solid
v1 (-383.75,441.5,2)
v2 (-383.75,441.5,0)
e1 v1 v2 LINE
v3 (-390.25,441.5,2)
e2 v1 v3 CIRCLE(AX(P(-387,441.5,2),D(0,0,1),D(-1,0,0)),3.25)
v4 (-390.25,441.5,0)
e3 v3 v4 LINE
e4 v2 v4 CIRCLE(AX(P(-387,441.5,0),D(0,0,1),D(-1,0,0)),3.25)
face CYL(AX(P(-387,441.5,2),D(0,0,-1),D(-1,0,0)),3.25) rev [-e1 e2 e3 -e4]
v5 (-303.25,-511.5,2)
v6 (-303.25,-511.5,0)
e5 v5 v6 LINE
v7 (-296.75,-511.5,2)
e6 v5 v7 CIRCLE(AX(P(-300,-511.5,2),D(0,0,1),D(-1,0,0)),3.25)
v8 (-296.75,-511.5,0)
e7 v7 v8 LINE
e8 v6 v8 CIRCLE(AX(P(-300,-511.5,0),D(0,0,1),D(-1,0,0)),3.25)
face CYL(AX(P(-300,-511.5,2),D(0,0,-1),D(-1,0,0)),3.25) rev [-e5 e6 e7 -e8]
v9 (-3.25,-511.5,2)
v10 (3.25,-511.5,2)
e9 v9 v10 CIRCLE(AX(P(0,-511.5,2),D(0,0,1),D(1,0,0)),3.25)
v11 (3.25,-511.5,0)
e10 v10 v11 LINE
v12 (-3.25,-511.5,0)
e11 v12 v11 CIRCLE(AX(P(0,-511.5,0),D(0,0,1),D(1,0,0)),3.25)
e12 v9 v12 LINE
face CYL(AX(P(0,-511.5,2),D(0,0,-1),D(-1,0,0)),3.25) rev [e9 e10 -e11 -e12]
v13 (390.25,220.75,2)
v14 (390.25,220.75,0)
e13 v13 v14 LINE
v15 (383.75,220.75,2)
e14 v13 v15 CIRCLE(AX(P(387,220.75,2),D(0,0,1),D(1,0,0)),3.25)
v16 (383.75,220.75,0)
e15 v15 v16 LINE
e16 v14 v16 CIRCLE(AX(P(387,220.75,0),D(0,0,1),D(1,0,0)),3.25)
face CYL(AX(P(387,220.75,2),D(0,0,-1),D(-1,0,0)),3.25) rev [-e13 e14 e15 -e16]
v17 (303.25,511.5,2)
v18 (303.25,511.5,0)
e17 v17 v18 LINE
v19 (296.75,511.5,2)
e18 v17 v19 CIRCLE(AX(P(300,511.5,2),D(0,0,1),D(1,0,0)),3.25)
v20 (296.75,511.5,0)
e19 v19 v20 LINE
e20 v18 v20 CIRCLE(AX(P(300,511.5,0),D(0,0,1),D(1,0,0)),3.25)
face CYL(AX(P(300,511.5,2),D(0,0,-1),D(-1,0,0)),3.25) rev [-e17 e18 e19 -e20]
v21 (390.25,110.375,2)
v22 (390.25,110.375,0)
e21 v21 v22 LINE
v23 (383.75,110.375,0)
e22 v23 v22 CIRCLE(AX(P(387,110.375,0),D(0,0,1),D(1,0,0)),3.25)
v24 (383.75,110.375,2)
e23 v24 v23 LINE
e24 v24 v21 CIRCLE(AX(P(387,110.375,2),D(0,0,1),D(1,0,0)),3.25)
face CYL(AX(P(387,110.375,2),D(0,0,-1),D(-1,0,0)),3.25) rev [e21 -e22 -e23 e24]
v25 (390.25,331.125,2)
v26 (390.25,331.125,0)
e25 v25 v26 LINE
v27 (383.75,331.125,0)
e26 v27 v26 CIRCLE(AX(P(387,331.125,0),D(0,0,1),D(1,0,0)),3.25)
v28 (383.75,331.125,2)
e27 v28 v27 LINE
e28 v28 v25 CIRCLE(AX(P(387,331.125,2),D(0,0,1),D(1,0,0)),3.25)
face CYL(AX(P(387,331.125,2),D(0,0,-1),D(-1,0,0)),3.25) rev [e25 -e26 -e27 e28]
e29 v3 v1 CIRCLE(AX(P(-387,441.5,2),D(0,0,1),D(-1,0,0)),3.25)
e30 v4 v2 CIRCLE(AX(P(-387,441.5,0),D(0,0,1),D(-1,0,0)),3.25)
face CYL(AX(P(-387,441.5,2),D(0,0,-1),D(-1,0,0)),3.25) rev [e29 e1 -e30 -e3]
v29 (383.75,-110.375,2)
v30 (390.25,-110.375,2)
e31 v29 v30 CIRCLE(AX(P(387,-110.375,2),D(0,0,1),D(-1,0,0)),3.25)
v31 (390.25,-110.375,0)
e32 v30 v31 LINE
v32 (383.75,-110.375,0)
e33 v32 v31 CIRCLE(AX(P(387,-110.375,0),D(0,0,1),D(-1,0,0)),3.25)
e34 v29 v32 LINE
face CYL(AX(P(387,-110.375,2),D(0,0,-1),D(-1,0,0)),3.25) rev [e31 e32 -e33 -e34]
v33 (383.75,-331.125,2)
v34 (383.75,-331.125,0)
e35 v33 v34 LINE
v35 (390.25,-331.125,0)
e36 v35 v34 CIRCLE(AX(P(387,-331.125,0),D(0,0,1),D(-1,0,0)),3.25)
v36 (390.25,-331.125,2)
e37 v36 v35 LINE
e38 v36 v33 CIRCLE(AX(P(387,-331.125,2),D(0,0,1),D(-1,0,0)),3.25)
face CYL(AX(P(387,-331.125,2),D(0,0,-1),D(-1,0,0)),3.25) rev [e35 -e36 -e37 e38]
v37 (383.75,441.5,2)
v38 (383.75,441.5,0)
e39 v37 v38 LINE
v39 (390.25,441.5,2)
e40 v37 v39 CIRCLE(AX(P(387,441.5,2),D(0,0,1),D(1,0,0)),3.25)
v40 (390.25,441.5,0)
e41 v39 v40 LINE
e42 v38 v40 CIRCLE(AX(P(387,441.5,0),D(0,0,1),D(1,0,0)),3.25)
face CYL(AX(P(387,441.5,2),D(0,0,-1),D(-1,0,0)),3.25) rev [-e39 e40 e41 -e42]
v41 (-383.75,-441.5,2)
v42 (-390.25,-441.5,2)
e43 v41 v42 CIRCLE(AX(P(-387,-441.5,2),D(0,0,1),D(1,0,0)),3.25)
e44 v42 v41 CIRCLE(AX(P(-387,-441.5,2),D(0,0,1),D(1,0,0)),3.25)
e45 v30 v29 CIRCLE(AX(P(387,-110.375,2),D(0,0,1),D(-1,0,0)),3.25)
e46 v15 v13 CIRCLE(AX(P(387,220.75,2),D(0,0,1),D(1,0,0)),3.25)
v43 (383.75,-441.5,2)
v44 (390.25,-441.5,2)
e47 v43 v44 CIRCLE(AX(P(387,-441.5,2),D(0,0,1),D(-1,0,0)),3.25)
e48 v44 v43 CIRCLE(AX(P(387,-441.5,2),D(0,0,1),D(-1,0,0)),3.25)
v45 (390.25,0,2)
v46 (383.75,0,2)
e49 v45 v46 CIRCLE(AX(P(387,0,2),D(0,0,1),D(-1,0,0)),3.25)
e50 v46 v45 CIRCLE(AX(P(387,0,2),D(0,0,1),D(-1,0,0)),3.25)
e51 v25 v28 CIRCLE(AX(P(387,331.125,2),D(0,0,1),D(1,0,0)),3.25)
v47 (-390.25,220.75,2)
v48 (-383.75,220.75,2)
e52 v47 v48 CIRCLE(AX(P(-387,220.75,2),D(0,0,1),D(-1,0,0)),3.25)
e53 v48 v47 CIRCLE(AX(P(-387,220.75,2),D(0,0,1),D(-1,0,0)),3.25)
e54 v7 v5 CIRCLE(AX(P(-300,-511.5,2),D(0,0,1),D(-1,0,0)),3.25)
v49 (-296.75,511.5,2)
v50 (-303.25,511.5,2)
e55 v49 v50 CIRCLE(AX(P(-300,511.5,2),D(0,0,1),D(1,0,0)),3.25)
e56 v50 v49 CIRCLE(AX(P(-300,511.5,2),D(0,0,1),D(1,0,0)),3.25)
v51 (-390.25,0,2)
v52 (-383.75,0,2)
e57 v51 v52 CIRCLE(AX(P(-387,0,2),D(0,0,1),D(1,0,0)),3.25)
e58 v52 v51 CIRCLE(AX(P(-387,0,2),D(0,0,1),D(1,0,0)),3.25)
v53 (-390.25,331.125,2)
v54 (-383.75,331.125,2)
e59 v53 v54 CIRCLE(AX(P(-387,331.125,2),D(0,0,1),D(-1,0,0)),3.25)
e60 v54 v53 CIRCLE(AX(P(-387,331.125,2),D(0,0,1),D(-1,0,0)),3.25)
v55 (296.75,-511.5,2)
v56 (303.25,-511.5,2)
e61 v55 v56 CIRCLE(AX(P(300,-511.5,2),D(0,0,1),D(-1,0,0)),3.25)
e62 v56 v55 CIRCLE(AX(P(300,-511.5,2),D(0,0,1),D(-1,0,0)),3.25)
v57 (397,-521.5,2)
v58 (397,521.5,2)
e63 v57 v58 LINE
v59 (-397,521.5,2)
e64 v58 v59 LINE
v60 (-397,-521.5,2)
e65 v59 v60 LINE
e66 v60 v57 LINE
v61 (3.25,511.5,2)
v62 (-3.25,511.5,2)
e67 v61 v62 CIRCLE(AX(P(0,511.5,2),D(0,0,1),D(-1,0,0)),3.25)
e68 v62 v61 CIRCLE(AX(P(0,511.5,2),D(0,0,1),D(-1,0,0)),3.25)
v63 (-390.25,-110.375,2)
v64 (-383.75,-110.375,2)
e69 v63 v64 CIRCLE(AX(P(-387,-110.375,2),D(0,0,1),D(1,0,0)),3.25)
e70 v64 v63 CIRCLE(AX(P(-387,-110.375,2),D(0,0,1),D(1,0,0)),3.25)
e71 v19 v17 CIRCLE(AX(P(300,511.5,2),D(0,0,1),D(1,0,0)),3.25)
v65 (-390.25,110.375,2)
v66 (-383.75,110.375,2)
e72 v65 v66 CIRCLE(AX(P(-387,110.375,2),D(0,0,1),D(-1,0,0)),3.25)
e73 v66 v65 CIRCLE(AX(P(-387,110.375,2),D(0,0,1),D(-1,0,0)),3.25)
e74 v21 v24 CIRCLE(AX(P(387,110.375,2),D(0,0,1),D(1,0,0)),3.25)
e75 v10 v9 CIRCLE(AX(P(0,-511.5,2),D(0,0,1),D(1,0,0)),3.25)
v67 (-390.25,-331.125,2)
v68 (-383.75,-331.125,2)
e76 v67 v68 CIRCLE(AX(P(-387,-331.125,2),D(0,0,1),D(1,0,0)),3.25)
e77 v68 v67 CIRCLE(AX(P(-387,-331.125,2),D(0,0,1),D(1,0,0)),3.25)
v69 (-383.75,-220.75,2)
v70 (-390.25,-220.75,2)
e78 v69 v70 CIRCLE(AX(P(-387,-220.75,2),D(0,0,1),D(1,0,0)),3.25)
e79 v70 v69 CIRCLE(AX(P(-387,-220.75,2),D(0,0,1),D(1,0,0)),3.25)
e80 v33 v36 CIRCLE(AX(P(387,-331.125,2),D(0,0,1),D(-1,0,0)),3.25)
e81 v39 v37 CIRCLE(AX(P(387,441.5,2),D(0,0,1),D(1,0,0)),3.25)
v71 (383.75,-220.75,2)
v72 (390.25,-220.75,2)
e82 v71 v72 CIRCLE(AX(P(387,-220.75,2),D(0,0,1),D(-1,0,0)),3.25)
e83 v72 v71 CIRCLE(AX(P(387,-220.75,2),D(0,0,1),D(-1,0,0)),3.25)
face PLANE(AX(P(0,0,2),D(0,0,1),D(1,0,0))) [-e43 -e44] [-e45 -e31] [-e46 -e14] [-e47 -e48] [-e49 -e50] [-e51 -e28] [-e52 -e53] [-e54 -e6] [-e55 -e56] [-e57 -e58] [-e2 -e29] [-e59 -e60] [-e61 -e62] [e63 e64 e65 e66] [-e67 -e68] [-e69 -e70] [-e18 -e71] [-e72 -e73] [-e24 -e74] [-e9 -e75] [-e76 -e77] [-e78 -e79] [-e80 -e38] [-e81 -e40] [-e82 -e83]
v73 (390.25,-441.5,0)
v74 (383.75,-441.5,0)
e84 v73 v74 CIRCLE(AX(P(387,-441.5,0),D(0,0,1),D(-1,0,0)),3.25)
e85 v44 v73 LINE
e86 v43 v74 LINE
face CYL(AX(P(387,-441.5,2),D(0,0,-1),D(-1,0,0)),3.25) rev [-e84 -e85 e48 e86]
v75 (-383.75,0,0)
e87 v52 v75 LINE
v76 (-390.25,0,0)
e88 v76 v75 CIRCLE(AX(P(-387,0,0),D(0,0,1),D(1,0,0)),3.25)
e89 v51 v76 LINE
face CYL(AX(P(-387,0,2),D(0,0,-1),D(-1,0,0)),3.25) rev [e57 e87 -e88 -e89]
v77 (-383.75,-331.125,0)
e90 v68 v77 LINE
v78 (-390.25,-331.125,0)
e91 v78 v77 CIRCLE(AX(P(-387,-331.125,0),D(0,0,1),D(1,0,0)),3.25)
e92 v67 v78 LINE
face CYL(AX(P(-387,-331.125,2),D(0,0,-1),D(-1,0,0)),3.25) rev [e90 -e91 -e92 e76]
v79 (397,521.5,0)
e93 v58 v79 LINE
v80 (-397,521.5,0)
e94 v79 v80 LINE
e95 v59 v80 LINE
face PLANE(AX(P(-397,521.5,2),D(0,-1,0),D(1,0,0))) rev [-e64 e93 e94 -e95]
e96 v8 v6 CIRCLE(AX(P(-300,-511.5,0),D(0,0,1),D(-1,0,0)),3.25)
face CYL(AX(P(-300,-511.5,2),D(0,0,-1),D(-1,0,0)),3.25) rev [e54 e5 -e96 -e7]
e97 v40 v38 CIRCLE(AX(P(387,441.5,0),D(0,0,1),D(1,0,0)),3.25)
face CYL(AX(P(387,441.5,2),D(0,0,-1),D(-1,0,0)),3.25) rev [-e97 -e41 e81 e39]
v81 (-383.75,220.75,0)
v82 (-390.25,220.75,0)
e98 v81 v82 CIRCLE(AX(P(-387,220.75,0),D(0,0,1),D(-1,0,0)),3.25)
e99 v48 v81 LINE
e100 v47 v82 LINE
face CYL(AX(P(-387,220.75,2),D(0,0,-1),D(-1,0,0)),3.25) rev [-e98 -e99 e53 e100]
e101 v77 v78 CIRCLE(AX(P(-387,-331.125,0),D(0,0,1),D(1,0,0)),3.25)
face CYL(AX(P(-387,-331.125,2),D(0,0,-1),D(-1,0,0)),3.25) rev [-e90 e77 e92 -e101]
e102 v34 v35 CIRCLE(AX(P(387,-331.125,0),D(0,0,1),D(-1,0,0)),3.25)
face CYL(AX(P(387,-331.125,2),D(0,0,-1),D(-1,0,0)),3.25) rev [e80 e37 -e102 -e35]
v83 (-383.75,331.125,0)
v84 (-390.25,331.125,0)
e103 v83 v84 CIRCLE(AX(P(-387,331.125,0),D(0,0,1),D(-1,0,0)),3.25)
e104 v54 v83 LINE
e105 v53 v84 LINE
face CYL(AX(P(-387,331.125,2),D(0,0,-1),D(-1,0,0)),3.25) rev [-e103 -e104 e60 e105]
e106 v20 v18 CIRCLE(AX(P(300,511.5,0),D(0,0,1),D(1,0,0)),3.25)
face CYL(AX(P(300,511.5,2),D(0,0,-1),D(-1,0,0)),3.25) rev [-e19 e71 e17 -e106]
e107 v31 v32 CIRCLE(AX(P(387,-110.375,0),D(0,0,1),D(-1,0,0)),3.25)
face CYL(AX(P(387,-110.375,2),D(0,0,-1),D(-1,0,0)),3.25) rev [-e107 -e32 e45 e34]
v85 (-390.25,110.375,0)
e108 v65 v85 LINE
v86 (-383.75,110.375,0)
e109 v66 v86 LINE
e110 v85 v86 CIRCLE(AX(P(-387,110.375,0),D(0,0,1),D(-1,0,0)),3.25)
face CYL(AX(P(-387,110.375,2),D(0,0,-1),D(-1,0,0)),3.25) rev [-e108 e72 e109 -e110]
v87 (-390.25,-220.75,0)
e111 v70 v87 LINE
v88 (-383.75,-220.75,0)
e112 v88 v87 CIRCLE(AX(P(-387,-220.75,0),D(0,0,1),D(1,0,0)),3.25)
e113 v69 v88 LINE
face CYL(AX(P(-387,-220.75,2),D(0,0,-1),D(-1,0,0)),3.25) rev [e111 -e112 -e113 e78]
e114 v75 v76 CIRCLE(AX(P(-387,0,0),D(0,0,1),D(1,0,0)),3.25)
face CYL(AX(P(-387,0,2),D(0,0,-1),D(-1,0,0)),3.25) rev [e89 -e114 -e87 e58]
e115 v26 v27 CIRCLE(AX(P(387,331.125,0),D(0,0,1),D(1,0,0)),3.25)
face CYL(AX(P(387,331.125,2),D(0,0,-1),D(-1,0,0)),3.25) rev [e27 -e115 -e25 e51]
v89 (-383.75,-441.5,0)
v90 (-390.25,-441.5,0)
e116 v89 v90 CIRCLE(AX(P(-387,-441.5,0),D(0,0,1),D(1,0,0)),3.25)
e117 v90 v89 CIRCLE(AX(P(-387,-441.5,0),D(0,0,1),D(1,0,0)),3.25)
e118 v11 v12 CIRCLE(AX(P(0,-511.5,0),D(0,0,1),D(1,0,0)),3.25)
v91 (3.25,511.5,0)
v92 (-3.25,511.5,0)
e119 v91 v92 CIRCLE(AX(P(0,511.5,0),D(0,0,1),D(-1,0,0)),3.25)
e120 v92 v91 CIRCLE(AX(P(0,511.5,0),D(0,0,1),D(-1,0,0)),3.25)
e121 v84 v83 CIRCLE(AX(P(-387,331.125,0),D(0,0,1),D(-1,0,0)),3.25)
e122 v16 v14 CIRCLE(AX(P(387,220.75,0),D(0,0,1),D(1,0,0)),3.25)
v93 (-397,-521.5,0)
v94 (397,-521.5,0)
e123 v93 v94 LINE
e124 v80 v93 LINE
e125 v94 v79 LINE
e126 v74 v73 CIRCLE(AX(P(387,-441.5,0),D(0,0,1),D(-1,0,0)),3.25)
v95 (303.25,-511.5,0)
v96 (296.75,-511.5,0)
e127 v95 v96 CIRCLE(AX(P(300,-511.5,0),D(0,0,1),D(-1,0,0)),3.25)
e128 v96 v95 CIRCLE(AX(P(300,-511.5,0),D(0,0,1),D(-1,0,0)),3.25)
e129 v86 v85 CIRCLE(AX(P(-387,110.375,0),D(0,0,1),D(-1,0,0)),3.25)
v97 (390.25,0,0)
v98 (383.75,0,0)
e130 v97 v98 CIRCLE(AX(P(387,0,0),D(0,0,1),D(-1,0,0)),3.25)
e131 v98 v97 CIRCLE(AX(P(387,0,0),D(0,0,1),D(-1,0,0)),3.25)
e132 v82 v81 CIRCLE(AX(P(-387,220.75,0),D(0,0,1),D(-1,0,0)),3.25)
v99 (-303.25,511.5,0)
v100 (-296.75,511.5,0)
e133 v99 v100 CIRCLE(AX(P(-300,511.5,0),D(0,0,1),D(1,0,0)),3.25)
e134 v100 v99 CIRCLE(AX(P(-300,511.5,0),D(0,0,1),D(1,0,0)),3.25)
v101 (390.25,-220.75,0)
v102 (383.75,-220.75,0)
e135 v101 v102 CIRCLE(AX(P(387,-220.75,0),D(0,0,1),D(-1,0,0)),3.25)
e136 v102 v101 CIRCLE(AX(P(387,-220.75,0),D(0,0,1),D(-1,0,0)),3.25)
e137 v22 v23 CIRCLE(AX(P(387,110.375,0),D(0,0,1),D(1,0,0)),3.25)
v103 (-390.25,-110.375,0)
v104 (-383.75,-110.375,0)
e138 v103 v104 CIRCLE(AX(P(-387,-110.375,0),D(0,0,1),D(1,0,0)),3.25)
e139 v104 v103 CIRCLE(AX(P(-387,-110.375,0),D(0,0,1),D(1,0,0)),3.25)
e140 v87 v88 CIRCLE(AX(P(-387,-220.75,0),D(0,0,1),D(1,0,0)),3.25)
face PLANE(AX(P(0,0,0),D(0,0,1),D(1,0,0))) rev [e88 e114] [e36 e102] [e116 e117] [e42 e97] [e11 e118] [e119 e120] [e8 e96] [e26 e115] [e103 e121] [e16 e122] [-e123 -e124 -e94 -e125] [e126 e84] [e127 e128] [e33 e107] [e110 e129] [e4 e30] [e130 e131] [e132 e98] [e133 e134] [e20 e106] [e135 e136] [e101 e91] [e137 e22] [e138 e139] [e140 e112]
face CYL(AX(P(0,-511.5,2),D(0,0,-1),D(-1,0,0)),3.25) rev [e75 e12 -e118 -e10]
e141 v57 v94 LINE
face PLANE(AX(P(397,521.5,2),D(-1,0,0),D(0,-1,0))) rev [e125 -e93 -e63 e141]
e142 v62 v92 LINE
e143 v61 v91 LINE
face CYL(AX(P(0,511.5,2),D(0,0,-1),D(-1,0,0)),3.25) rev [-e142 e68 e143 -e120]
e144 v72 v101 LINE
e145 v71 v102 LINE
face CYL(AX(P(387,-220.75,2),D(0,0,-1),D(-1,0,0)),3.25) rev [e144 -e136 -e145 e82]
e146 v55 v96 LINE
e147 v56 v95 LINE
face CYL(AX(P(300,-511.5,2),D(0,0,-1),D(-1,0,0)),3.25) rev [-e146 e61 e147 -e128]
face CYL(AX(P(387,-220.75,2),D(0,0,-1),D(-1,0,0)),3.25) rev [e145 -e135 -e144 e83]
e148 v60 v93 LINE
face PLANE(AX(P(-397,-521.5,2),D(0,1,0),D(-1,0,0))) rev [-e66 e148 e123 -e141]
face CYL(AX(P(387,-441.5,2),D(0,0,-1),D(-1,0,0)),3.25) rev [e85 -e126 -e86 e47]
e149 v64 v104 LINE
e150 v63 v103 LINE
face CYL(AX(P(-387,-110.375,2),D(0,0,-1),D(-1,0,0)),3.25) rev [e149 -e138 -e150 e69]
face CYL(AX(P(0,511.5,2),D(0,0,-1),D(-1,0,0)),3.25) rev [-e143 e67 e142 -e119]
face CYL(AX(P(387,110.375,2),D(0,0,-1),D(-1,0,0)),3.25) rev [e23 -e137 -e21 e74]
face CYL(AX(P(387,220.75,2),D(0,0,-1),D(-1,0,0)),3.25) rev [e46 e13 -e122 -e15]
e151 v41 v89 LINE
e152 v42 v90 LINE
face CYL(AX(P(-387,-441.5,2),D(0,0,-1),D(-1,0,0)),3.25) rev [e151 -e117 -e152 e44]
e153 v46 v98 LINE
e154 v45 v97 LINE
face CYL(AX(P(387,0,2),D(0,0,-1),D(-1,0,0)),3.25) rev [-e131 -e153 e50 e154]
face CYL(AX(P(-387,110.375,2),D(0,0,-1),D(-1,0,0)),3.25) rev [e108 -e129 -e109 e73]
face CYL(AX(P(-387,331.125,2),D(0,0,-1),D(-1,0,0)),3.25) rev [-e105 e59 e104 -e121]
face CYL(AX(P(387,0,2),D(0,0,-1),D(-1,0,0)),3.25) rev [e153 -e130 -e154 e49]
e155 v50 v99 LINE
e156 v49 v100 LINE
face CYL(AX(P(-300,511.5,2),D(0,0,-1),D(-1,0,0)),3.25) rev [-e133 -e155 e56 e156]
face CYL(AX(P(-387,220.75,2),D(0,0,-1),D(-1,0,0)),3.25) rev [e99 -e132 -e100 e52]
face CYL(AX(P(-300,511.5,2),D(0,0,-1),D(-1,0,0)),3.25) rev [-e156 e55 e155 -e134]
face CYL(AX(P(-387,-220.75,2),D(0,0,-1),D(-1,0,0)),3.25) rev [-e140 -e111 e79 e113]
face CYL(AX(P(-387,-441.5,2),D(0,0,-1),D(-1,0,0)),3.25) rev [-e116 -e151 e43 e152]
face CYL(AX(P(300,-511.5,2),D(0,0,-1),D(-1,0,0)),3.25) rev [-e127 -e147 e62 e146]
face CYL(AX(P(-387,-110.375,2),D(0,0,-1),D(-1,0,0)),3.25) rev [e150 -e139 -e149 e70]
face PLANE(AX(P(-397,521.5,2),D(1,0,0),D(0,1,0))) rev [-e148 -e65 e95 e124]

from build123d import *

# Parameters (mm, degrees)
SKETCH_1_W      = 794
SKETCH_1_H      = 1043
SKETCH_1_R      = 3.25
EXTRUDE_1_DEPTH = 2


with BuildPart() as part:
    # 草图1 → 凸台-拉伸1 (new body)
    with BuildSketch(Plane.XY):
        Rectangle(SKETCH_1_W, SKETCH_1_H)
        with Locations((-387, 0)):
            Circle(SKETCH_1_R, mode=Mode.SUBTRACT)
        with Locations((-387, -110.375)):
            Circle(SKETCH_1_R, mode=Mode.SUBTRACT)
        with Locations((-387, -220.75)):
            Circle(SKETCH_1_R, mode=Mode.SUBTRACT)
        with Locations((-387, -331.125)):
            Circle(SKETCH_1_R, mode=Mode.SUBTRACT)
        with Locations((-387, -441.5)):
            Circle(SKETCH_1_R, mode=Mode.SUBTRACT)
        with Locations((0, -511.5)):
            Circle(SKETCH_1_R, mode=Mode.SUBTRACT)
        with Locations(Location((0, 511.5, 0), (0, 0, 180))):
            Circle(SKETCH_1_R, mode=Mode.SUBTRACT)
        with Locations(Location((-387, 441.5, 0), (0, 0, 180))):
            Circle(SKETCH_1_R, mode=Mode.SUBTRACT)
        with Locations(Location((-387, 331.125, 0), (0, 0, 180))):
            Circle(SKETCH_1_R, mode=Mode.SUBTRACT)
        with Locations(Location((-387, 220.75, 0), (0, 0, 180))):
            Circle(SKETCH_1_R, mode=Mode.SUBTRACT)
        with Locations(Location((-387, 110.375, 0), (0, 0, 180))):
            Circle(SKETCH_1_R, mode=Mode.SUBTRACT)
        with Locations((387, 110.375)):
            Circle(SKETCH_1_R, mode=Mode.SUBTRACT)
        with Locations((387, 220.75)):
            Circle(SKETCH_1_R, mode=Mode.SUBTRACT)
        with Locations((387, 331.125)):
            Circle(SKETCH_1_R, mode=Mode.SUBTRACT)
        with Locations((387, 441.5)):
            Circle(SKETCH_1_R, mode=Mode.SUBTRACT)
        with Locations(Location((387, -441.5, 0), (0, 0, 180))):
            Circle(SKETCH_1_R, mode=Mode.SUBTRACT)
        with Locations(Location((387, -331.125, 0), (0, 0, 180))):
            Circle(SKETCH_1_R, mode=Mode.SUBTRACT)
        with Locations(Location((387, -220.75, 0), (0, 0, 180))):
            Circle(SKETCH_1_R, mode=Mode.SUBTRACT)
        with Locations(Location((387, -110.375, 0), (0, 0, 180))):
            Circle(SKETCH_1_R, mode=Mode.SUBTRACT)
        with Locations(Location((387, 0, 0), (0, 0, 180))):
            Circle(SKETCH_1_R, mode=Mode.SUBTRACT)
        with Locations((-300, 511.5)):
            Circle(SKETCH_1_R, mode=Mode.SUBTRACT)
        with Locations((300, 511.5)):
            Circle(SKETCH_1_R, mode=Mode.SUBTRACT)
        with Locations(Location((300, -511.5, 0), (0, 0, 180))):
            Circle(SKETCH_1_R, mode=Mode.SUBTRACT)
        with Locations(Location((-300, -511.5, 0), (0, 0, 180))):
            Circle(SKETCH_1_R, mode=Mode.SUBTRACT)
    extrude(amount=EXTRUDE_1_DEPTH)


solid = part.part
